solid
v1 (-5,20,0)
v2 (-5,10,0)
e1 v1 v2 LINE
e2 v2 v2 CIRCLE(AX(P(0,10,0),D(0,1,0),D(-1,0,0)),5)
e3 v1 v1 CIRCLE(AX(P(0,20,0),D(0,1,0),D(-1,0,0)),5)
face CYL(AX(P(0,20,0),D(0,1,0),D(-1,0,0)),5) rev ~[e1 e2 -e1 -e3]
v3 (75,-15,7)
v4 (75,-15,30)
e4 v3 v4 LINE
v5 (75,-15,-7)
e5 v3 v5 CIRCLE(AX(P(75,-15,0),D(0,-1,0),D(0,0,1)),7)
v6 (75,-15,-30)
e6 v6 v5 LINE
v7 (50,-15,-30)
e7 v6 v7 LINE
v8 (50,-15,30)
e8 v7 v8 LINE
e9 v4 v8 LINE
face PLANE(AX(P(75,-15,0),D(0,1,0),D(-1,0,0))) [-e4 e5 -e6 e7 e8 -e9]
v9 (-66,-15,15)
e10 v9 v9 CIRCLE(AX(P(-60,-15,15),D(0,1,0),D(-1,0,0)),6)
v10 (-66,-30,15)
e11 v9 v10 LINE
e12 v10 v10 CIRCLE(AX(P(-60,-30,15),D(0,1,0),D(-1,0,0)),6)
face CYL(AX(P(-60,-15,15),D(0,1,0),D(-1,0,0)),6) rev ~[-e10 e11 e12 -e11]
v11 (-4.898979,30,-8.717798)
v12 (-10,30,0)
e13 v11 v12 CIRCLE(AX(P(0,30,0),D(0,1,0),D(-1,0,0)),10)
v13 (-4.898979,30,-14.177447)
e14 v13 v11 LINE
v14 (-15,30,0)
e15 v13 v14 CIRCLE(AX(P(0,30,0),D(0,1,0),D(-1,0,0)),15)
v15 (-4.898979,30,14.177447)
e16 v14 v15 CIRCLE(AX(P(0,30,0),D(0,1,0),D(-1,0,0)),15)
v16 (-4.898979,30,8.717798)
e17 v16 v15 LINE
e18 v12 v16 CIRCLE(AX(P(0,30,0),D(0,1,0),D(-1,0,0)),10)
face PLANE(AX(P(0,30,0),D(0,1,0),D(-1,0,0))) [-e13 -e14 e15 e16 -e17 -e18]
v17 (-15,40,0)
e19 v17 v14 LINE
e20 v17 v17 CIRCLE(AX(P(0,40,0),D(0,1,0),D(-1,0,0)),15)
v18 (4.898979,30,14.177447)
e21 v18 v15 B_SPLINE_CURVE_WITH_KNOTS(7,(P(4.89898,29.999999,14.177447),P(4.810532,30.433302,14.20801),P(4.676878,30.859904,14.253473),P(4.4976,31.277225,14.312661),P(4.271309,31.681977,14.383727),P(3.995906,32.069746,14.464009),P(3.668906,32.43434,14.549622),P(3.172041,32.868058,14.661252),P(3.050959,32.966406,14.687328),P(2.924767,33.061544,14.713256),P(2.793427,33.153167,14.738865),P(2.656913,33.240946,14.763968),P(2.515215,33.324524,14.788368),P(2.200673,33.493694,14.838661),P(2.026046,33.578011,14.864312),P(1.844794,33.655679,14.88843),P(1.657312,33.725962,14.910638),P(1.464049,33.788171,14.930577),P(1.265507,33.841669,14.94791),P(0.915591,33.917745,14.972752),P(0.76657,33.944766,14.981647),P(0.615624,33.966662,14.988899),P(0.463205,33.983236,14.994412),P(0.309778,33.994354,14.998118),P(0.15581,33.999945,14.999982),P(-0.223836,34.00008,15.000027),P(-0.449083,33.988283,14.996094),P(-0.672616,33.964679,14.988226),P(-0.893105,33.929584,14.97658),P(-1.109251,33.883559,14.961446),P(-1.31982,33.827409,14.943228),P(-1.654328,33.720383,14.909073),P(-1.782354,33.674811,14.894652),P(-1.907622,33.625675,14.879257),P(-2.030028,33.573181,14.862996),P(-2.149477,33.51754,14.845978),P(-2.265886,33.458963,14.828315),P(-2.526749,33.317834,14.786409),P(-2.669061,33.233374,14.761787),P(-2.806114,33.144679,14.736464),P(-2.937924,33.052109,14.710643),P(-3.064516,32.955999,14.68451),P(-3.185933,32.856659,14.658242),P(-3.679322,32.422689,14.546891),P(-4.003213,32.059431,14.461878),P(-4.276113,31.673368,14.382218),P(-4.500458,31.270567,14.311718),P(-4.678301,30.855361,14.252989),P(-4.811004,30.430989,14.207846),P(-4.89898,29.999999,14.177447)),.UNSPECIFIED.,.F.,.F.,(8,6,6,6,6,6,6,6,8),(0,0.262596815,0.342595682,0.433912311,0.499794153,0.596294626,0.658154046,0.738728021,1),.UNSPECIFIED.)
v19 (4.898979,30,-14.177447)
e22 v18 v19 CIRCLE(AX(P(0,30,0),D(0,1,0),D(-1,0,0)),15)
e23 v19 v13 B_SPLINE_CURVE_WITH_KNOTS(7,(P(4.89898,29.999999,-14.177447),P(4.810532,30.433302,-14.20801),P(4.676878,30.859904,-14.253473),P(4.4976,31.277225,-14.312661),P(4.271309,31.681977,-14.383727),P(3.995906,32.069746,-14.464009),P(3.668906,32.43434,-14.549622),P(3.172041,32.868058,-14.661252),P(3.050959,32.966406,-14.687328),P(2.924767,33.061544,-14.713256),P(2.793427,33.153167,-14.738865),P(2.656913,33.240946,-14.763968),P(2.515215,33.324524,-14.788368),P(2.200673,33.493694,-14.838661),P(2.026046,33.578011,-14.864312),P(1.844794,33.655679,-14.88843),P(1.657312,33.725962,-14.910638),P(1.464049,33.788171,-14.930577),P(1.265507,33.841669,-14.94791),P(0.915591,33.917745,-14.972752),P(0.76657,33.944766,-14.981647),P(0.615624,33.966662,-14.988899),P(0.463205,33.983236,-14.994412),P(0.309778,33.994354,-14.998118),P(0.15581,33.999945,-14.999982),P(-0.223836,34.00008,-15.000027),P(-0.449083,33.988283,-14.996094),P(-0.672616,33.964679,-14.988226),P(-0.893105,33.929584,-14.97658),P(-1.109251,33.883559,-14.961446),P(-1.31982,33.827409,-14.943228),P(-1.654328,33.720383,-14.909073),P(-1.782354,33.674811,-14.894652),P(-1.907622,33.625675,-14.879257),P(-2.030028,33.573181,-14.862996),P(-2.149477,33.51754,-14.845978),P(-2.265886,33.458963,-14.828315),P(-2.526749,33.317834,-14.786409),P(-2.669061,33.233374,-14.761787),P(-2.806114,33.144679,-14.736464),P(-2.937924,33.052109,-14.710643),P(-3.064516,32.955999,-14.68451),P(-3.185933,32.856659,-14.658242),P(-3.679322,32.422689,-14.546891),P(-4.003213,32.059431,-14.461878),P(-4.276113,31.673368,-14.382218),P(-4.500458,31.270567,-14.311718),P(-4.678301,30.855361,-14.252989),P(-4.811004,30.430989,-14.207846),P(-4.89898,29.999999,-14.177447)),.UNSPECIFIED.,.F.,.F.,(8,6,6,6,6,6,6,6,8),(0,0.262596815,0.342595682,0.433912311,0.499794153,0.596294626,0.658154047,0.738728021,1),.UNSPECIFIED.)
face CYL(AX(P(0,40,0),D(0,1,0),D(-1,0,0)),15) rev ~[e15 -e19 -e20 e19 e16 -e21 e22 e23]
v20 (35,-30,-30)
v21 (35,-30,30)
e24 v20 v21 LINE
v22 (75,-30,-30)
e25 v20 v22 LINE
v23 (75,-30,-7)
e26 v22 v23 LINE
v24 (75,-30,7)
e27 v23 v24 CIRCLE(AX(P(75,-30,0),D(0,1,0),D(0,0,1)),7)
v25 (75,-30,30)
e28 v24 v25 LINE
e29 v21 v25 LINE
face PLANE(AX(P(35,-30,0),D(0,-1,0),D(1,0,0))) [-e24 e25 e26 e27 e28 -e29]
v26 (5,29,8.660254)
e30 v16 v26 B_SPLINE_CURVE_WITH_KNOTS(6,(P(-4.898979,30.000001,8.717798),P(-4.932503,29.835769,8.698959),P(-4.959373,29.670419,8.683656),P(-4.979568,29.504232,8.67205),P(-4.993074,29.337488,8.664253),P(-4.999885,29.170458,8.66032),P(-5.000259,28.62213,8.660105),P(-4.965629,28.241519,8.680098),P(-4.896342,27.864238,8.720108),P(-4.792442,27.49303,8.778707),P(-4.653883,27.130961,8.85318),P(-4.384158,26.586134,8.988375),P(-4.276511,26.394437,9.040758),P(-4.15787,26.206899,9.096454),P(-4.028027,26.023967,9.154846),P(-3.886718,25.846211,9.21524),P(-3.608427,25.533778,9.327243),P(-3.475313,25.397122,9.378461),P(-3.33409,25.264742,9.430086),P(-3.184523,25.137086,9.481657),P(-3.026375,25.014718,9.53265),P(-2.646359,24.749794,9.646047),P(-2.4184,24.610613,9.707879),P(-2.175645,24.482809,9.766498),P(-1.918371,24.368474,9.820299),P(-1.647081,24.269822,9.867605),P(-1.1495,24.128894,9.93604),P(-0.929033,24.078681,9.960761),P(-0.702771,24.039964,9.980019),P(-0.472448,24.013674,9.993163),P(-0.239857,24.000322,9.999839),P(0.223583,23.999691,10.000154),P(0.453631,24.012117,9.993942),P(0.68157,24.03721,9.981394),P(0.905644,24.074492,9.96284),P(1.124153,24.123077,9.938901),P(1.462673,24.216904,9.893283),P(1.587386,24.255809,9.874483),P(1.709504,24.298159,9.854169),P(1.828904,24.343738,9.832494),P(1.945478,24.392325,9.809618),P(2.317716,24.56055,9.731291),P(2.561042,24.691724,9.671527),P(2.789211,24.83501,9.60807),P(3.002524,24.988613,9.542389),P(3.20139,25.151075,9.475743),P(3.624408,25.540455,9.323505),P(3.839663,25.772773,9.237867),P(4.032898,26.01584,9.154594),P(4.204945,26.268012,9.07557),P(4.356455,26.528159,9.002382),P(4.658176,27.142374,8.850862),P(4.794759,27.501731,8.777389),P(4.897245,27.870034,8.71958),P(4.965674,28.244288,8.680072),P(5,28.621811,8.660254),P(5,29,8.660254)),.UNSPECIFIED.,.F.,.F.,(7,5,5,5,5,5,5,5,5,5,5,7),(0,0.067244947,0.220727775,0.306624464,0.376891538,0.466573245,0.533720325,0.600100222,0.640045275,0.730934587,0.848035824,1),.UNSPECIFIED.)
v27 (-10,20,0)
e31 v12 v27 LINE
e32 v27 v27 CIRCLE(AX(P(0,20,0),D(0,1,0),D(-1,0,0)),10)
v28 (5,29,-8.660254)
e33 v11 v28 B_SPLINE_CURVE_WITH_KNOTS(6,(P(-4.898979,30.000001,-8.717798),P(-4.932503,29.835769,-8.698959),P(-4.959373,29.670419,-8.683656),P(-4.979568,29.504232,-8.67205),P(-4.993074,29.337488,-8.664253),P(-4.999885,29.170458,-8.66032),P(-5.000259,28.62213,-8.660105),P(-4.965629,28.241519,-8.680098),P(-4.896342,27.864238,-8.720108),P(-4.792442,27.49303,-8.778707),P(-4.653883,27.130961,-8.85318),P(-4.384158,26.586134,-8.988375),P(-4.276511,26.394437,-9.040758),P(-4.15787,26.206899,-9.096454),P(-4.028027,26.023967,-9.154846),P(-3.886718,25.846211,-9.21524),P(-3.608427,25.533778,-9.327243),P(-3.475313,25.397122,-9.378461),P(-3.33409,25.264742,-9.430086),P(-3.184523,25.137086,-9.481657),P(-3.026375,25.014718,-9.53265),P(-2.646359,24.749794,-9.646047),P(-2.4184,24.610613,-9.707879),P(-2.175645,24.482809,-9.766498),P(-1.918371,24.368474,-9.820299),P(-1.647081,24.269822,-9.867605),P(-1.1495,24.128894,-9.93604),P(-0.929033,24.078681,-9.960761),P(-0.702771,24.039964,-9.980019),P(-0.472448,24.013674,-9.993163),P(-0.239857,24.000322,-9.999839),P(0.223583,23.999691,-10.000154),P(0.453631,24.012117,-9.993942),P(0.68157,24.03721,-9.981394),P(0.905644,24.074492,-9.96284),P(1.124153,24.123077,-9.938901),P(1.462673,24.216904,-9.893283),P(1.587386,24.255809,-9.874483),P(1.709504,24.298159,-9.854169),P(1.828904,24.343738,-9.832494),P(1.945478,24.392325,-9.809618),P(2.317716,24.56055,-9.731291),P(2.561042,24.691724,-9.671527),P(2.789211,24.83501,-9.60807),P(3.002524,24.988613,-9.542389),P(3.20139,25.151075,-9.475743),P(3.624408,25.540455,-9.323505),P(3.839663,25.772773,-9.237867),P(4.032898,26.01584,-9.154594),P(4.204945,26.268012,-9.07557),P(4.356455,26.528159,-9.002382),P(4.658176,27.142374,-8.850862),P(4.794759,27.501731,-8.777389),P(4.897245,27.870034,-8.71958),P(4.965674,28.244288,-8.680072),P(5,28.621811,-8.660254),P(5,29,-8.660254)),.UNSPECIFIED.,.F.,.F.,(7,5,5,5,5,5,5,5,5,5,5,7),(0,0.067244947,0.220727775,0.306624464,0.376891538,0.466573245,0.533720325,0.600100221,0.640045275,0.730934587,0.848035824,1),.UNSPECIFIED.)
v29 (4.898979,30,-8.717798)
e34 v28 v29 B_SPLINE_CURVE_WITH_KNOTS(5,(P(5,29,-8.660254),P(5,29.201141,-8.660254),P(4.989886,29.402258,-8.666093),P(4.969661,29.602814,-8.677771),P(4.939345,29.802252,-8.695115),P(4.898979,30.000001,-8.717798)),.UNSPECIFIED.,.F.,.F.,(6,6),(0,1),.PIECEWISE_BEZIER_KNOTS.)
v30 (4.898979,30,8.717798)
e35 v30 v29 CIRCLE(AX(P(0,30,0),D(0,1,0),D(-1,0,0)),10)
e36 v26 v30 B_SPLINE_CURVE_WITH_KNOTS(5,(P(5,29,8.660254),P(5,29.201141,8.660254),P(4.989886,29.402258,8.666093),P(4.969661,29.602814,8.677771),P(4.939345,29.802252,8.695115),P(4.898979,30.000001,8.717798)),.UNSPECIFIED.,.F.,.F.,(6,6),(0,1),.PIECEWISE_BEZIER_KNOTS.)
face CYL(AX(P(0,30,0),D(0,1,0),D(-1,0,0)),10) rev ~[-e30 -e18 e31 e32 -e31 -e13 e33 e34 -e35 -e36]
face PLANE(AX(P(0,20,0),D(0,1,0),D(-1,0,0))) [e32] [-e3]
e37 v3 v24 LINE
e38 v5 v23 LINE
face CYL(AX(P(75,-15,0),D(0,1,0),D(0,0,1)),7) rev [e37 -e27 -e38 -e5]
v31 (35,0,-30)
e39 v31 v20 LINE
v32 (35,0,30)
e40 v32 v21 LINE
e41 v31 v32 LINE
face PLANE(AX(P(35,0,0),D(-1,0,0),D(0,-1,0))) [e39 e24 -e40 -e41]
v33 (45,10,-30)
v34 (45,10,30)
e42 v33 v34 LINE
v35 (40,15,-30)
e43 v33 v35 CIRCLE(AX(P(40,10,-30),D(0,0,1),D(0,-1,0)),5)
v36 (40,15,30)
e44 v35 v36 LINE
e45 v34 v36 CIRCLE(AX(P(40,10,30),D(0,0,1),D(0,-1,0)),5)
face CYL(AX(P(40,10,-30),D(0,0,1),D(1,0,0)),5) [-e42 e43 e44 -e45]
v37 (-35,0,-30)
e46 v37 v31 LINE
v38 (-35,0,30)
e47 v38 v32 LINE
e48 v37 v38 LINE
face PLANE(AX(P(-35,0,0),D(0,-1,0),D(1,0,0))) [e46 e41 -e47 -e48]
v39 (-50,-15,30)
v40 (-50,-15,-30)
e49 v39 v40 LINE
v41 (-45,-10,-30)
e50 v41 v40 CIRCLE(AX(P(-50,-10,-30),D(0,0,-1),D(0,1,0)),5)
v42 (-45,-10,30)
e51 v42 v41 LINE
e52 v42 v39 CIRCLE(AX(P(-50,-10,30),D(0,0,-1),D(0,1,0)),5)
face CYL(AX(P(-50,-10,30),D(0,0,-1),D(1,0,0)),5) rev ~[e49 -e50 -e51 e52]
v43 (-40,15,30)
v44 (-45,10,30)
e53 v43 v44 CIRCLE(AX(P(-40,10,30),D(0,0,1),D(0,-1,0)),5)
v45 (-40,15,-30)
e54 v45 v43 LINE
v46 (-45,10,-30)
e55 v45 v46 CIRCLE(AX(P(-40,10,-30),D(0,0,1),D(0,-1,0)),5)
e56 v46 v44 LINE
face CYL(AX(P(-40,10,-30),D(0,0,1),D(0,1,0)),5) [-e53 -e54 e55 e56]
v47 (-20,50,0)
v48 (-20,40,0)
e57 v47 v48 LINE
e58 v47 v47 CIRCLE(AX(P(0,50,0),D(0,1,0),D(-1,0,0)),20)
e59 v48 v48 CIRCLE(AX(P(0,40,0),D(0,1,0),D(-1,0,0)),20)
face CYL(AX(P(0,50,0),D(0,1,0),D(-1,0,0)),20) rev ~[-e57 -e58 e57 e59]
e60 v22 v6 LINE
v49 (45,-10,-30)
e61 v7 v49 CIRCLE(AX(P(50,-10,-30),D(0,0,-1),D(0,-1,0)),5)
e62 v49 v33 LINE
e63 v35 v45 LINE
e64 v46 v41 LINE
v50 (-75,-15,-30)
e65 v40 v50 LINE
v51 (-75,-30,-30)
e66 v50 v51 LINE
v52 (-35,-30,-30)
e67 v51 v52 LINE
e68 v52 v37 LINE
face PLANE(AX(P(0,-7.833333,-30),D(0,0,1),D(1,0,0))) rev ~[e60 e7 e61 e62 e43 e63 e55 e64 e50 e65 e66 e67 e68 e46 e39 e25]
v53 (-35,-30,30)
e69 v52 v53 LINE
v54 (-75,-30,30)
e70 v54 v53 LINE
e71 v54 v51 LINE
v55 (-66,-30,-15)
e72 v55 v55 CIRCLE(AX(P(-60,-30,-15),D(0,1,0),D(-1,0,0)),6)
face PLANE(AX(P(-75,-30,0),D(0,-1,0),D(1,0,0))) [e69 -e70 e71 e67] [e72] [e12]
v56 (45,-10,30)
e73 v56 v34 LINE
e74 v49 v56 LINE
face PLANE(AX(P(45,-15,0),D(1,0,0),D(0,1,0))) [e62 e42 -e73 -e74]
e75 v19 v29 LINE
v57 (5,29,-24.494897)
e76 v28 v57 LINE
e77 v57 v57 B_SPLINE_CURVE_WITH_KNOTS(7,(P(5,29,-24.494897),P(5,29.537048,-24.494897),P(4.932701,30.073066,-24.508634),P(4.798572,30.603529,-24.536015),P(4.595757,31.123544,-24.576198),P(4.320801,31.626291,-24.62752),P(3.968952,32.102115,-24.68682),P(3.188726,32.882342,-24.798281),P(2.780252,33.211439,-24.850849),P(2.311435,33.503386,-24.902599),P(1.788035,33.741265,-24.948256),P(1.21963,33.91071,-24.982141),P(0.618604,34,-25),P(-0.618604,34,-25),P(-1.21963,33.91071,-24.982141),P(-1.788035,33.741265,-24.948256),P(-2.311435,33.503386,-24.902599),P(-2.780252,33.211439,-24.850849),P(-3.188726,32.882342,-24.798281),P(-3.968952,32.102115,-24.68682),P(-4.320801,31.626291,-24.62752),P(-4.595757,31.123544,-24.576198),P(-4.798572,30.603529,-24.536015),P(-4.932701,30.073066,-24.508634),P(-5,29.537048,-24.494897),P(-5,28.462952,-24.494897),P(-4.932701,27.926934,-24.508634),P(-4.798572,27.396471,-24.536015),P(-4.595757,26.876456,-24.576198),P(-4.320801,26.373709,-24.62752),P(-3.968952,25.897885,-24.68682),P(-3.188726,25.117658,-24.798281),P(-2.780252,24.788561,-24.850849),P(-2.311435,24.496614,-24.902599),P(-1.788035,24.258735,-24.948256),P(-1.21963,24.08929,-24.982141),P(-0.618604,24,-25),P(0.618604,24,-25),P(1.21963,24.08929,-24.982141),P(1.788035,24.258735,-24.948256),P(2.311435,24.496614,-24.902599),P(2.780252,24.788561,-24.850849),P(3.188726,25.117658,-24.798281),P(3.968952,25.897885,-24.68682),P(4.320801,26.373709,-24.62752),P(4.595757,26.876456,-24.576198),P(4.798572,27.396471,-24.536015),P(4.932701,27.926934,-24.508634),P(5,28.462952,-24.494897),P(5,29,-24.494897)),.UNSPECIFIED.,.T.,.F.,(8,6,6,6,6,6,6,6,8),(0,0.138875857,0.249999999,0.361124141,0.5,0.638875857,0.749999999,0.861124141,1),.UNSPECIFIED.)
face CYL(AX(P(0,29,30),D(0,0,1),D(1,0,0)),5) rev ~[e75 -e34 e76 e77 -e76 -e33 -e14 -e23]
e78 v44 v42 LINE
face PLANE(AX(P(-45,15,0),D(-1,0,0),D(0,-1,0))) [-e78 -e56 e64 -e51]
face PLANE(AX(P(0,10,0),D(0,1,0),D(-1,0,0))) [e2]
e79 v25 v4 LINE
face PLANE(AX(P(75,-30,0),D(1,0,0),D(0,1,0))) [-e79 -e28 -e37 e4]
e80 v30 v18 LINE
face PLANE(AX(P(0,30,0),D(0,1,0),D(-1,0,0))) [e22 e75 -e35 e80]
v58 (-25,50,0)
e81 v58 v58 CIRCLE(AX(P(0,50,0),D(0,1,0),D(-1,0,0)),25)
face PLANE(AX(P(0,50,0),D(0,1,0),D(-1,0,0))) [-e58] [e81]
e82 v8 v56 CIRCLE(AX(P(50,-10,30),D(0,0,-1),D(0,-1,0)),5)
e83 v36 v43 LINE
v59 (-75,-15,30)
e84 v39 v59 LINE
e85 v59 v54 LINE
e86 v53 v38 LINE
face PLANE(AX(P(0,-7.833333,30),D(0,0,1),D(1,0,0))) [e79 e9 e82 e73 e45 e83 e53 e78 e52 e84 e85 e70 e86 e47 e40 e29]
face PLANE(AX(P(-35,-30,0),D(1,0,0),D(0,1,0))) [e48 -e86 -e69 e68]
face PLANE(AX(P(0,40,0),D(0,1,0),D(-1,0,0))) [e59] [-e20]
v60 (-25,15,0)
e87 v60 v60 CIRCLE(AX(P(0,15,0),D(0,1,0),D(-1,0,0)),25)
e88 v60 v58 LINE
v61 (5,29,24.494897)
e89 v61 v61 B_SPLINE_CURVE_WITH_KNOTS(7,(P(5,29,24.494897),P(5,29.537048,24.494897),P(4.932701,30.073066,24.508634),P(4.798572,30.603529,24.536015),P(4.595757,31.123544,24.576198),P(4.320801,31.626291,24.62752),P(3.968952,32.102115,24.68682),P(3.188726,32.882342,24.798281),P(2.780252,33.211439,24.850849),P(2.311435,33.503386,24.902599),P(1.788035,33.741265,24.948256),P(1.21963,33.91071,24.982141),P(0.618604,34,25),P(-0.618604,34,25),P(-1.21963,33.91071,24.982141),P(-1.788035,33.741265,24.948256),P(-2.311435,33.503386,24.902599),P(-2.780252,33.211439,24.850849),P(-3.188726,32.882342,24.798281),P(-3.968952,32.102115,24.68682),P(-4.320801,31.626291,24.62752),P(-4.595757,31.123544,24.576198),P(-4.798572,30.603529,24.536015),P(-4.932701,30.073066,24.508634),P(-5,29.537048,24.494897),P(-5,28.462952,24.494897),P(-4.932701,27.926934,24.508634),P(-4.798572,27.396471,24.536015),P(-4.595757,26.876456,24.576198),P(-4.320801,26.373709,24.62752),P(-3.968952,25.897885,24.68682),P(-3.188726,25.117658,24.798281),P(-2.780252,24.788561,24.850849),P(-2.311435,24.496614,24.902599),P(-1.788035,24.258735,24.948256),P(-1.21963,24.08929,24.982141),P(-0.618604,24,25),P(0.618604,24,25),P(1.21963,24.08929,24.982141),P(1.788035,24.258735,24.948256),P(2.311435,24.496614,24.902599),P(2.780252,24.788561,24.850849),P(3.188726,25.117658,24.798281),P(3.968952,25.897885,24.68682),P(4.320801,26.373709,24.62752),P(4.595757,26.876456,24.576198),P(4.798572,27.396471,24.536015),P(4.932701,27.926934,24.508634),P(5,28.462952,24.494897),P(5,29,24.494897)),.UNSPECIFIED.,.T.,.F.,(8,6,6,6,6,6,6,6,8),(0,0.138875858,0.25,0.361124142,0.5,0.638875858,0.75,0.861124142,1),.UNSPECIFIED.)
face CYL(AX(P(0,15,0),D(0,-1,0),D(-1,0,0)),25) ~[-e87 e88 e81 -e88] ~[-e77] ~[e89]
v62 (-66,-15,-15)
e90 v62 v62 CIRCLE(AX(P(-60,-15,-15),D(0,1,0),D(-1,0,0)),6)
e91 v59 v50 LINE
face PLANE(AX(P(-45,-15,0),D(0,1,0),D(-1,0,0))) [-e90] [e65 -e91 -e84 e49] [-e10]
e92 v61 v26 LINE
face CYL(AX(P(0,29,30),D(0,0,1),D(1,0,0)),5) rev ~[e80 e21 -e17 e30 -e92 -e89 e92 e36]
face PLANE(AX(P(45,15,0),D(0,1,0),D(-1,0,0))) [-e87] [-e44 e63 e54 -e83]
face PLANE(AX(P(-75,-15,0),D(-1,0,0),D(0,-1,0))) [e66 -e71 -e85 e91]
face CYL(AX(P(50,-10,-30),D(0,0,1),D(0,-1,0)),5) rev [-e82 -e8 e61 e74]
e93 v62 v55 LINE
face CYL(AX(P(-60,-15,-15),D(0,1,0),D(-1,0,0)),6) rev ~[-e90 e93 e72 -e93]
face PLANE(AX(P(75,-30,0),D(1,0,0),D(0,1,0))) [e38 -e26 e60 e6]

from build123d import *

# Parameters (mm, degrees)
BRACKET_BODY_DEPTH    = 30
FOOT_SLOT_A_REACH     = 88.168
FOOT_SLOT_A_SKETCH_R  = 6
FOOT_SLOT_B_REACH     = 88.168
BEARING_BOSS_SKETCH_R = 25
BEARING_BOSS_DEPTH    = 35
BORE_STEP_1_SKETCH_R  = 20
BORE_STEP_1_DEPTH     = 10
BORE_STEP_2_SKETCH_R  = 15
BORE_STEP_2_DEPTH     = 10
BORE_STEP_3_SKETCH_R  = 10
BORE_STEP_3_DEPTH     = 10
BORE_STEP_4_SKETCH_R  = 5
BORE_STEP_4_DEPTH     = 10
CROSS_HOLE_SKETCH_R   = 5
CROSS_HOLE_DEPTH      = 109.282039139
BEND_FILLET_R5_A_R    = 5
BEND_FILLET_R5_B_R    = 5
BEND_FILLET_R5_C_R    = 5


with BuildPart() as part:
    # Bracket Profile Sketch → Bracket Body (new, symmetric)
    with BuildSketch(Plane.XY):
        Polygon((-75, -30), (-35, -30), (-35, 0), (35, 0), (35, -30), (75, -30), (75, -15), (45, -15), (45, 15), (-45, 15), (-45, -15), (-75, -15), align=None)
    extrude(amount=BRACKET_BODY_DEPTH, both=True)

    # Foot Slot A Sketch → Foot Slot A (cut, up to next)
    with BuildSketch(Plane(origin=(0, -15, 0), x_dir=(1, 0, 0), z_dir=(0, 1, 0)), mode=Mode.PRIVATE) as foot_slot_a_sk1:
        with Locations(Location((-60, 15, 0), (0, 0, 180))):
            Circle(FOOT_SLOT_A_SKETCH_R)
    foot_slot_a_tool1 = extrude(foot_slot_a_sk1.sketch, amount=-FOOT_SLOT_A_REACH, mode=Mode.PRIVATE) & part.part
    # Foot Slot A Sketch → Foot Slot A (cut, up to next)
    with BuildSketch(Plane(origin=(0, -15, 0), x_dir=(1, 0, 0), z_dir=(0, 1, 0)), mode=Mode.PRIVATE) as foot_slot_a_sk2:
        with Locations(Location((-60, -15, 0), (0, 0, 180))):
            Circle(FOOT_SLOT_A_SKETCH_R)
    foot_slot_a_tool2 = extrude(foot_slot_a_sk2.sketch, amount=-FOOT_SLOT_A_REACH, mode=Mode.PRIVATE) & part.part
    add(foot_slot_a_tool1.solids().sort_by_distance((-60, -15, -15))[0], mode=Mode.SUBTRACT)
    add(foot_slot_a_tool2.solids().sort_by_distance((-60, -15, 15))[0], mode=Mode.SUBTRACT)

    # Foot Slot B Sketch → Foot Slot B (cut, up to next)
    with BuildSketch(Plane(origin=(0, -15, 0), x_dir=(1, 0, 0), z_dir=(0, 1, 0)), mode=Mode.PRIVATE) as foot_slot_b_sk1:
        with BuildLine():
            Line((75, 7), (75, -7))
            ThreePointArc((75, -7), (68, 0), (75, 7))
        make_face()
    foot_slot_b_tool1 = extrude(foot_slot_b_sk1.sketch, amount=-FOOT_SLOT_B_REACH, mode=Mode.PRIVATE) & part.part
    add(foot_slot_b_tool1.solids().sort_by_distance((72.029108, -15, 0))[0], mode=Mode.SUBTRACT)

    # Bearing Boss Sketch → Bearing Boss (add)
    with BuildSketch(Plane(origin=(0, 15, 0), x_dir=(1, 0, 0), z_dir=(0, 1, 0))):
        with Locations(Location((0, 0, 0), (0, 0, 180))):
            Circle(BEARING_BOSS_SKETCH_R)
    extrude(amount=BEARING_BOSS_DEPTH)

    # Bore Step 1 Sketch → Bore Step 1 (cut)
    with BuildSketch(Plane(origin=(0, 50, 0), x_dir=(1, 0, 0), z_dir=(0, 1, 0))):
        with Locations(Location((0, 0, 0), (0, 0, 180))):
            Circle(BORE_STEP_1_SKETCH_R)
    extrude(amount=-BORE_STEP_1_DEPTH, mode=Mode.SUBTRACT)

    # Bore Step 2 Sketch → Bore Step 2 (cut)
    with BuildSketch(Plane(origin=(0, 40, 0), x_dir=(1, 0, 0), z_dir=(0, 1, 0))):
        with Locations(Location((0, 0, 0), (0, 0, 180))):
            Circle(BORE_STEP_2_SKETCH_R)
    extrude(amount=-BORE_STEP_2_DEPTH, mode=Mode.SUBTRACT)

    # Bore Step 3 Sketch → Bore Step 3 (cut)
    with BuildSketch(Plane(origin=(0, 30, 0), x_dir=(1, 0, 0), z_dir=(0, 1, 0))):
        with Locations(Location((0, 0, 0), (0, 0, 180))):
            Circle(BORE_STEP_3_SKETCH_R)
    extrude(amount=-BORE_STEP_3_DEPTH, mode=Mode.SUBTRACT)

    # Bore Step 4 Sketch → Bore Step 4 (cut)
    with BuildSketch(Plane(origin=(0, 20, 0), x_dir=(1, 0, 0), z_dir=(0, 1, 0))):
        with Locations(Location((0, 0, 0), (0, 0, 180))):
            Circle(BORE_STEP_4_SKETCH_R)
    extrude(amount=-BORE_STEP_4_DEPTH, mode=Mode.SUBTRACT)

    # Cross Hole Sketch → Cross Hole (cut, through all)
    with BuildSketch(Plane.XY.offset(30)):
        with Locations((0, 29)):
            Circle(CROSS_HOLE_SKETCH_R)
    extrude(amount=-CROSS_HOLE_DEPTH, mode=Mode.SUBTRACT)

    # Bend Fillet R5 A
    bend_fillet_r5_a_edges = [part.edges().sort_by_distance(p)[0] for p in [
        (45, -15, 0),
    ]]
    fillet(bend_fillet_r5_a_edges, radius=BEND_FILLET_R5_A_R)

    # Bend Fillet R5 B
    bend_fillet_r5_b_edges = [part.edges().sort_by_distance(p)[0] for p in [
        (-45, 15, 0),
        (45, 15, 0),
    ]]
    fillet(bend_fillet_r5_b_edges, radius=BEND_FILLET_R5_B_R)

    # Bend Fillet R5 C
    bend_fillet_r5_c_edges = [part.edges().sort_by_distance(p)[0] for p in [
        (-45, -15, 0),
    ]]
    fillet(bend_fillet_r5_c_edges, radius=BEND_FILLET_R5_C_R)


solid = part.part
